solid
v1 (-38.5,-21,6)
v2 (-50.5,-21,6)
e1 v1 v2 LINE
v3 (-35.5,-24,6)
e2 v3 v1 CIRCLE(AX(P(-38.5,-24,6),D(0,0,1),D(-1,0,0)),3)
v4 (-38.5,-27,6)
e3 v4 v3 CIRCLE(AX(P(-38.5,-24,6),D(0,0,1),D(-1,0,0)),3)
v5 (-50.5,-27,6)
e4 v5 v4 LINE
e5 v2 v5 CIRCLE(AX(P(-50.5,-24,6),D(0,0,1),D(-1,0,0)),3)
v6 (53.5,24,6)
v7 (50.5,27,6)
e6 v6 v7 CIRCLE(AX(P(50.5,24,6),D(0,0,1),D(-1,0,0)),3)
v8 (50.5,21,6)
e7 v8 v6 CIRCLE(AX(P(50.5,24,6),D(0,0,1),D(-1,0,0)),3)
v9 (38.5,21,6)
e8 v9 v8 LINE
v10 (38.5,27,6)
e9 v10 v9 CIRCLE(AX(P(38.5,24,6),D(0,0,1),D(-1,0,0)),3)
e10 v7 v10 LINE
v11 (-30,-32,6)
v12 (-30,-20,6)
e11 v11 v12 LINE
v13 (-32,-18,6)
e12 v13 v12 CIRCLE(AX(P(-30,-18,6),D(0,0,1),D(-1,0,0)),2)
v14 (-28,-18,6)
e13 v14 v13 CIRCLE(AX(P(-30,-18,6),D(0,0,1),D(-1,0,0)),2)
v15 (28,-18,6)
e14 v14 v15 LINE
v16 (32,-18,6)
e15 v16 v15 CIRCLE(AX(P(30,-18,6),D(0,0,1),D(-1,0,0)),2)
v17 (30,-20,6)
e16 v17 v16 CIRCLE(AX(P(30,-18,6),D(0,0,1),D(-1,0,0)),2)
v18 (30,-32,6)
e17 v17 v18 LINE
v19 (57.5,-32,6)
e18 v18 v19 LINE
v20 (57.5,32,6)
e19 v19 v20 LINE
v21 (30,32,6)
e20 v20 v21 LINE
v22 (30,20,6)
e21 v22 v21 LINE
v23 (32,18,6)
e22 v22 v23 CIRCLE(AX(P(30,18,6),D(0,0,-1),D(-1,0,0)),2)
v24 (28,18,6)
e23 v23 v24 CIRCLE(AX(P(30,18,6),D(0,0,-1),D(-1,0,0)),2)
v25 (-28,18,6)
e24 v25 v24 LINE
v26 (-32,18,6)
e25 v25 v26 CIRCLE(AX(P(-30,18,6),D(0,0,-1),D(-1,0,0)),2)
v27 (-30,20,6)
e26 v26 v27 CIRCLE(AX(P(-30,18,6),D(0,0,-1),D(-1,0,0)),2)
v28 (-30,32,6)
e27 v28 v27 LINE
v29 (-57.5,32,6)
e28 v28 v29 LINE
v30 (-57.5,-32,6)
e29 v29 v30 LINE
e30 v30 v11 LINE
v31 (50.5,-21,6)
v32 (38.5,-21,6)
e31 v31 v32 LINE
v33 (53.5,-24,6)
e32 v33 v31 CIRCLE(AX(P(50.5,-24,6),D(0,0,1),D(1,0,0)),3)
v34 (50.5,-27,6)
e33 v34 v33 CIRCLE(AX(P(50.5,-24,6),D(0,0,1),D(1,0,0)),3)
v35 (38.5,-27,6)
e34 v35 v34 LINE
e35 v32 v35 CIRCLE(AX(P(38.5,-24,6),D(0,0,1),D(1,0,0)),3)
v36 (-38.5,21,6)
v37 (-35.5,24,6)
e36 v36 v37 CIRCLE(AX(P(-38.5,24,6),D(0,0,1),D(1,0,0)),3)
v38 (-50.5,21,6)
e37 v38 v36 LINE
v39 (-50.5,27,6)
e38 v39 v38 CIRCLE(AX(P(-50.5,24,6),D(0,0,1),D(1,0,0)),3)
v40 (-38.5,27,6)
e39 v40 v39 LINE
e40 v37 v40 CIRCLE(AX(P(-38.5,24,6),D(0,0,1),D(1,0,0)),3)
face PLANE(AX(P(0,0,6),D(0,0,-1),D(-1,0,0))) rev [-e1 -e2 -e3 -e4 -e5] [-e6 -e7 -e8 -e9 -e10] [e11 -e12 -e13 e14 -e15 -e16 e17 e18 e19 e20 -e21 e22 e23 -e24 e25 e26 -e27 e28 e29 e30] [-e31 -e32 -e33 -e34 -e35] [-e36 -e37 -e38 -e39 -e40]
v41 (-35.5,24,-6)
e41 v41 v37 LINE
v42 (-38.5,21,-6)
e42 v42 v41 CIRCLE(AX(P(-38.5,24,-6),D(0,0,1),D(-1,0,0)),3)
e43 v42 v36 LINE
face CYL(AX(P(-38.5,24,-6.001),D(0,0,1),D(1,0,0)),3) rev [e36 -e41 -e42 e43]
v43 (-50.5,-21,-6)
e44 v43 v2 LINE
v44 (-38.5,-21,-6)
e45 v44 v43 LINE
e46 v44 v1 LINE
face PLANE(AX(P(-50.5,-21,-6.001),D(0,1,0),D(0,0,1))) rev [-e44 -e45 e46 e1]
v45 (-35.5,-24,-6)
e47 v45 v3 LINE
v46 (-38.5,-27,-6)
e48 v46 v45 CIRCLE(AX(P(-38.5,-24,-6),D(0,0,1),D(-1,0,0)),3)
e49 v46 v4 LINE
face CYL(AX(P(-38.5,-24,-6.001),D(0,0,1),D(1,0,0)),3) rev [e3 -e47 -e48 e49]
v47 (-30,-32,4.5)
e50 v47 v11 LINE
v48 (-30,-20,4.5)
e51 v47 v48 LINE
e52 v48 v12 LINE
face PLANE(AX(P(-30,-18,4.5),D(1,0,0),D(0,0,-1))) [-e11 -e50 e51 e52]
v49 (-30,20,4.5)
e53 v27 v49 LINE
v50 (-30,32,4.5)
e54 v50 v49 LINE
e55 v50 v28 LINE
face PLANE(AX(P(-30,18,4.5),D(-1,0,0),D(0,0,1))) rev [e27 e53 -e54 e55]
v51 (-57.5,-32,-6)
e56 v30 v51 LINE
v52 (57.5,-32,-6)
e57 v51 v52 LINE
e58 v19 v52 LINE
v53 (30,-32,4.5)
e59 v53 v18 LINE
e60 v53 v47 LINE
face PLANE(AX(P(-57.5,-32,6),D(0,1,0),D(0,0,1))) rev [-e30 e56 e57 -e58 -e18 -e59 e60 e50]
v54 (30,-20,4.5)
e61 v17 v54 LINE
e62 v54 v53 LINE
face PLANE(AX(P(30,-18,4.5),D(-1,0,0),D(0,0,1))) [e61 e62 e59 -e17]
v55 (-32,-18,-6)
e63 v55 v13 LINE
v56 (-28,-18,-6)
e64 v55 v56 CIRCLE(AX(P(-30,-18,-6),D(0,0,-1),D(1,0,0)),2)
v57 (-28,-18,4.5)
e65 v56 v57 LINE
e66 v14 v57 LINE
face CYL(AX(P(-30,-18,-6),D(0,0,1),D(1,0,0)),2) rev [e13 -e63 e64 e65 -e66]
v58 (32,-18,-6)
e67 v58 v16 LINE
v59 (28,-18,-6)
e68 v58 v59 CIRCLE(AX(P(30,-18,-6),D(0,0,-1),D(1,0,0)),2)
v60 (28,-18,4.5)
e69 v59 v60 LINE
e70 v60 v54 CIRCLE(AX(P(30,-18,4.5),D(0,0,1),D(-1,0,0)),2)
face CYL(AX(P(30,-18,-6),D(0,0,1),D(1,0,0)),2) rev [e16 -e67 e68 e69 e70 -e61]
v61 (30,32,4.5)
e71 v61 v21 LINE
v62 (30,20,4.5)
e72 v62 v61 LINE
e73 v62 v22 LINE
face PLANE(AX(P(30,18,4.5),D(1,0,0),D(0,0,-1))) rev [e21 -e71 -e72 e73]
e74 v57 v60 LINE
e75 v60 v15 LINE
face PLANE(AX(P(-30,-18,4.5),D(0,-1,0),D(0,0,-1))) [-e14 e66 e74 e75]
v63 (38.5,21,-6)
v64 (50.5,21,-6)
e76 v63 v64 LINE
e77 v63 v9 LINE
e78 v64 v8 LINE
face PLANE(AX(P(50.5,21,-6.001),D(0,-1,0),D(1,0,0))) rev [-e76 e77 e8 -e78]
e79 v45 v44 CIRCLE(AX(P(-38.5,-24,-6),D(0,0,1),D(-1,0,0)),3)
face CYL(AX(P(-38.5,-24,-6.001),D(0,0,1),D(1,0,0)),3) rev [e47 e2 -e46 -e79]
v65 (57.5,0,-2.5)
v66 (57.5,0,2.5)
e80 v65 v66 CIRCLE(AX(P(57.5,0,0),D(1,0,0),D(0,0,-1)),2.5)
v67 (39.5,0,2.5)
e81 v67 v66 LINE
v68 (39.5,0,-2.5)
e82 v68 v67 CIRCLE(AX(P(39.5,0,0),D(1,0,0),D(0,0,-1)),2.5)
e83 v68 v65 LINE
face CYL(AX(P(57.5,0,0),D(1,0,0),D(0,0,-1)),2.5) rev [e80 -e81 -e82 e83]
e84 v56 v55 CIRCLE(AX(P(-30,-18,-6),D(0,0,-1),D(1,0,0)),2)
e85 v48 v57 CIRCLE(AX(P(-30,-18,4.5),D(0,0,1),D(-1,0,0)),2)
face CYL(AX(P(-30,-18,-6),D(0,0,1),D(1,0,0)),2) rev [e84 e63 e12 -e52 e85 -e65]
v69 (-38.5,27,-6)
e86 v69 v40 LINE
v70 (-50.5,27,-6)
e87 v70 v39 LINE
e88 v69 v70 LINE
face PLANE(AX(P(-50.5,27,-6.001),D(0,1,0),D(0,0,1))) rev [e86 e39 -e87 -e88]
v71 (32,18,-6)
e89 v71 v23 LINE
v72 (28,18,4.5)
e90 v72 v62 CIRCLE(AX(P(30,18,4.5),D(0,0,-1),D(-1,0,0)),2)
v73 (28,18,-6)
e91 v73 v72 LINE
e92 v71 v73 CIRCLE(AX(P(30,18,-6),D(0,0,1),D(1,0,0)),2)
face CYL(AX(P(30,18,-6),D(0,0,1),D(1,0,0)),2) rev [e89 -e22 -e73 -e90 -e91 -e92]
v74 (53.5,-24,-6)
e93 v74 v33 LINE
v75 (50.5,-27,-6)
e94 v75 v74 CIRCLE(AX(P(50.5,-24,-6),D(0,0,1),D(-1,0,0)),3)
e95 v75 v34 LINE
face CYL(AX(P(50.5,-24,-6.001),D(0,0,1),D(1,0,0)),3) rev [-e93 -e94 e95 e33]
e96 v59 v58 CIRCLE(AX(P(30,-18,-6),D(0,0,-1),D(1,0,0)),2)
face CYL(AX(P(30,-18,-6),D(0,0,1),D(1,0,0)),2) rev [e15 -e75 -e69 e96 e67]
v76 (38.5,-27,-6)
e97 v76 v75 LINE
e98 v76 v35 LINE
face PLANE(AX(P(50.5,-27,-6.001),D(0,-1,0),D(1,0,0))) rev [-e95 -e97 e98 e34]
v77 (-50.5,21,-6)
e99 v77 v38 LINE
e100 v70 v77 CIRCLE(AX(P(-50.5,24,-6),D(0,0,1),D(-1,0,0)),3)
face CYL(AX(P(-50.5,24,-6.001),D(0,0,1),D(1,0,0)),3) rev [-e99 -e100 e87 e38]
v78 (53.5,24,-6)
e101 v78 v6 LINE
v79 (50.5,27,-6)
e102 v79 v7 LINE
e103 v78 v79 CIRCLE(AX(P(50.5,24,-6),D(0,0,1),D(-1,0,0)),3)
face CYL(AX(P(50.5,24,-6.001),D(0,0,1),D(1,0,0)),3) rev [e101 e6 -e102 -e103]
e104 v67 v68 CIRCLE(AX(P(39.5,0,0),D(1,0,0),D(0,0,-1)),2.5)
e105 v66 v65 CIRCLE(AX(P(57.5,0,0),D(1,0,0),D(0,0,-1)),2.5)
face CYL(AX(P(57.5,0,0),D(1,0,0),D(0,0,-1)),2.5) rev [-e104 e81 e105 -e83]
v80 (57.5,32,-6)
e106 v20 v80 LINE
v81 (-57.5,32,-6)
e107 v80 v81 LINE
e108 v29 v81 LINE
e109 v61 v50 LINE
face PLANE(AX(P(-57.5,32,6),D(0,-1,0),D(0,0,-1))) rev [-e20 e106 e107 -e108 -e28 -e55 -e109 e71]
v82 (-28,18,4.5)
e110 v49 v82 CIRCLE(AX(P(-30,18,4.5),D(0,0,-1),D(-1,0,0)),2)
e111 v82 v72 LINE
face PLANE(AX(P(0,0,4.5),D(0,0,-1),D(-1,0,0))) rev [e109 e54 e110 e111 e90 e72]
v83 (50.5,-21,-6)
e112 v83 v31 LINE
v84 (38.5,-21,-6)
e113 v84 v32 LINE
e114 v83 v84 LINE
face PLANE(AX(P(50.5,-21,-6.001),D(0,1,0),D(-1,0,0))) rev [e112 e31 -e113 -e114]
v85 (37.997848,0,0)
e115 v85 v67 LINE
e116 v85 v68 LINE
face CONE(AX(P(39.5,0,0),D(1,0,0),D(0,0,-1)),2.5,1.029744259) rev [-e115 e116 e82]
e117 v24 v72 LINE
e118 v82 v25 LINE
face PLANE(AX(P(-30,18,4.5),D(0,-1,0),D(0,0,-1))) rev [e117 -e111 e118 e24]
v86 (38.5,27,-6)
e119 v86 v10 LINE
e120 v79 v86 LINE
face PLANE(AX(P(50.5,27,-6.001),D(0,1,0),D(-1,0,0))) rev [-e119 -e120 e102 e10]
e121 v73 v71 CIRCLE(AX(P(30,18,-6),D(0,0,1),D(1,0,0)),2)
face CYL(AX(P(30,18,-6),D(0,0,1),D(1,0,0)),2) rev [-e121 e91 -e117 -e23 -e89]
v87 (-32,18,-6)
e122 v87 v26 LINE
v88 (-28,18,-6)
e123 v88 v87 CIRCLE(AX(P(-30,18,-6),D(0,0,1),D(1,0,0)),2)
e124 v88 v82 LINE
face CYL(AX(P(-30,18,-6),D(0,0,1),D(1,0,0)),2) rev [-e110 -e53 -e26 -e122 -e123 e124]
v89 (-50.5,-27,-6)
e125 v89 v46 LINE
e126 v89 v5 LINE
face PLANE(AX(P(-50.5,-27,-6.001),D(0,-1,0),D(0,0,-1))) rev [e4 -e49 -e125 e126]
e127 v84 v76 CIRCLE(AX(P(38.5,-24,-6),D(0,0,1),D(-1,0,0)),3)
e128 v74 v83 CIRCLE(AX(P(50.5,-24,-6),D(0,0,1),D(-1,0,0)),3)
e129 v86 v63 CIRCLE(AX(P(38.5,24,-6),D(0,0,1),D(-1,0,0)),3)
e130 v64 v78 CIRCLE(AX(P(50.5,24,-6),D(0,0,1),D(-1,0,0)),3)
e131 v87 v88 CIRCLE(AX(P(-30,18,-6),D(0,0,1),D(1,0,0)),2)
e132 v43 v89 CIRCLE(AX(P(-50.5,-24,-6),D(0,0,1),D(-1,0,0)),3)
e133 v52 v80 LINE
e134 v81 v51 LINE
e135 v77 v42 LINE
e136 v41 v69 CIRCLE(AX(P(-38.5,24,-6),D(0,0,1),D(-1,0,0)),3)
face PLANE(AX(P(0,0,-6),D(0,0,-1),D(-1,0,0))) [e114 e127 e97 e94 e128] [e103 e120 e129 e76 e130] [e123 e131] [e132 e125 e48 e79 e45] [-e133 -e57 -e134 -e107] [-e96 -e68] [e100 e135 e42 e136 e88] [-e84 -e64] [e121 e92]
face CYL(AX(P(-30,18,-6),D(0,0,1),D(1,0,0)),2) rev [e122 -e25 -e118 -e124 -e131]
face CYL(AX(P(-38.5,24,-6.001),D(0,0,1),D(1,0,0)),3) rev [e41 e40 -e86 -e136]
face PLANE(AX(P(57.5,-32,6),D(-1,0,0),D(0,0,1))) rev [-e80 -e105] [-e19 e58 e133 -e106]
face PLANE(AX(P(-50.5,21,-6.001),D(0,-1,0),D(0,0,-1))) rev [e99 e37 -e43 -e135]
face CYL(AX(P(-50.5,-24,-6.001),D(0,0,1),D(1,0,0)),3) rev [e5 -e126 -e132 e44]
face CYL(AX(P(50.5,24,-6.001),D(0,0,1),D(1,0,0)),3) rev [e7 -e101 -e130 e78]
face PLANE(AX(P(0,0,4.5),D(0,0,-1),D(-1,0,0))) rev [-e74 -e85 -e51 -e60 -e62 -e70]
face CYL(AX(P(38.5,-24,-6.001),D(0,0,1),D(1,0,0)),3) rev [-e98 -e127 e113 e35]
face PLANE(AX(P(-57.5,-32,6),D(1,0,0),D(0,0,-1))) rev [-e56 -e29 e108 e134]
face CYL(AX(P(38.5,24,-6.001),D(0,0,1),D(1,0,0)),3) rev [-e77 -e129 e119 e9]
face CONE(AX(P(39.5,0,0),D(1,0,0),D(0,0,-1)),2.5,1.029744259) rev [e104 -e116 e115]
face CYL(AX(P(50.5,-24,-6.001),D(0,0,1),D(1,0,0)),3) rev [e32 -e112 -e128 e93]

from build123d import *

# Parameters (mm, degrees)
SKETCH_1_W             = 115
SKETCH_1_H             = 64
EXTRUDE_1_DEPTH        = 6
SKETCH_2_W             = 60
SKETCH_2_H             = 14
CUT_EXTRUDE_1_DEPTH    = 1.5
SKETCH_3_R             = 2
CUT_EXTRUDE_2_DEPTH    = 67.889834803
CUT_EXTRUDE_3_REACH    = 68.89
HOLE_WIZARD_M6_1_D     = 5
HOLE_WIZARD_M6_1_DEPTH = 18
HOLE_WIZARD_M6_1_TIP   = 1.502151548


with BuildPart() as part:
    # 草图1 → 凸台-拉伸1 (new, symmetric)
    with BuildSketch(Plane.XY):
        Rectangle(SKETCH_1_W, SKETCH_1_H)
    extrude(amount=EXTRUDE_1_DEPTH, both=True)

    # 草图2 → 切除-拉伸1 (cut)
    with BuildSketch(Plane.XY.offset(6)):
        with Locations((0, 25)):
            Rectangle(SKETCH_2_W, SKETCH_2_H)
    cut_extrude_1 = extrude(amount=-CUT_EXTRUDE_1_DEPTH, mode=Mode.SUBTRACT)

    # 草图3 → 切除-拉伸2 (cut, symmetric)
    with BuildSketch(Plane.XY.offset(6)):
        with Locations((-30, 18)):
            Circle(SKETCH_3_R)
        with Locations((30, 18)):
            Circle(SKETCH_3_R)
    cut_extrude_2 = extrude(amount=CUT_EXTRUDE_2_DEPTH, both=True, mode=Mode.SUBTRACT)

    # 镜向1: 切除-拉伸1, 切除-拉伸2 across plane
    add(cut_extrude_1.mirror(Plane.ZX), mode=Mode.SUBTRACT)
    add(cut_extrude_2.mirror(Plane.ZX), mode=Mode.SUBTRACT)

    # 草图4 → 切除-拉伸3 (cut, up to next)
    with BuildSketch(Plane.XY.offset(6), mode=Mode.PRIVATE) as cut_extrude_3_sk1:
        with BuildLine():
            Line((-50.5, 27), (-38.5, 27))
            ThreePointArc((-38.5, 27), (-35.5, 24), (-38.5, 21))
            Line((-38.5, 21), (-50.5, 21))
            ThreePointArc((-50.5, 21), (-53.5, 24), (-50.5, 27))
        make_face()
    cut_extrude_3_tool1 = extrude(cut_extrude_3_sk1.sketch, amount=-CUT_EXTRUDE_3_REACH, mode=Mode.PRIVATE) & part.part
    # 草图4 → 切除-拉伸3 (cut, up to next)
    with BuildSketch(Plane.XY.offset(6), mode=Mode.PRIVATE) as cut_extrude_3_sk2:
        with BuildLine():
            Line((50.5, 27), (38.5, 27))
            ThreePointArc((38.5, 27), (35.5, 24), (38.5, 21))
            Line((38.5, 21), (50.5, 21))
            ThreePointArc((50.5, 21), (53.5, 24), (50.5, 27))
        make_face()
    cut_extrude_3_tool2 = extrude(cut_extrude_3_sk2.sketch, amount=-CUT_EXTRUDE_3_REACH, mode=Mode.PRIVATE) & part.part
    # 草图4 → 切除-拉伸3 (cut, up to next)
    with BuildSketch(Plane.XY.offset(6), mode=Mode.PRIVATE) as cut_extrude_3_sk3:
        with BuildLine():
            Line((-50.5, -27), (-38.5, -27))
            ThreePointArc((-38.5, -27), (-35.5, -24), (-38.5, -21))
            Line((-38.5, -21), (-50.5, -21))
            ThreePointArc((-50.5, -21), (-53.5, -24), (-50.5, -27))
        make_face()
    cut_extrude_3_tool3 = extrude(cut_extrude_3_sk3.sketch, amount=-CUT_EXTRUDE_3_REACH, mode=Mode.PRIVATE) & part.part
    # 草图4 → 切除-拉伸3 (cut, up to next)
    with BuildSketch(Plane.XY.offset(6), mode=Mode.PRIVATE) as cut_extrude_3_sk4:
        with BuildLine():
            Line((50.5, -27), (38.5, -27))
            ThreePointArc((38.5, -27), (35.5, -24), (38.5, -21))
            Line((38.5, -21), (50.5, -21))
            ThreePointArc((50.5, -21), (53.5, -24), (50.5, -27))
        make_face()
    cut_extrude_3_tool4 = extrude(cut_extrude_3_sk4.sketch, amount=-CUT_EXTRUDE_3_REACH, mode=Mode.PRIVATE) & part.part
    add(cut_extrude_3_tool1.solids().sort_by_distance((-44.5, 24, 6))[0], mode=Mode.SUBTRACT)
    add(cut_extrude_3_tool2.solids().sort_by_distance((44.5, 24, 6))[0], mode=Mode.SUBTRACT)
    add(cut_extrude_3_tool3.solids().sort_by_distance((-44.5, -24, 6))[0], mode=Mode.SUBTRACT)
    add(cut_extrude_3_tool4.solids().sort_by_distance((44.5, -24, 6))[0], mode=Mode.SUBTRACT)

    # M6 螺纹孔1
    with Locations(Plane(origin=(57.5, 0, 0), x_dir=(0, 0, 1), z_dir=(1, 0, 0))):
        with Locations((0, 0)):
            Hole(HOLE_WIZARD_M6_1_D / 2, depth=HOLE_WIZARD_M6_1_DEPTH)
            with Locations((0, 0, -(HOLE_WIZARD_M6_1_DEPTH + HOLE_WIZARD_M6_1_TIP / 2))):  # 118° drill point
                Cone(0, HOLE_WIZARD_M6_1_D / 2, HOLE_WIZARD_M6_1_TIP, mode=Mode.SUBTRACT)


solid = part.part
